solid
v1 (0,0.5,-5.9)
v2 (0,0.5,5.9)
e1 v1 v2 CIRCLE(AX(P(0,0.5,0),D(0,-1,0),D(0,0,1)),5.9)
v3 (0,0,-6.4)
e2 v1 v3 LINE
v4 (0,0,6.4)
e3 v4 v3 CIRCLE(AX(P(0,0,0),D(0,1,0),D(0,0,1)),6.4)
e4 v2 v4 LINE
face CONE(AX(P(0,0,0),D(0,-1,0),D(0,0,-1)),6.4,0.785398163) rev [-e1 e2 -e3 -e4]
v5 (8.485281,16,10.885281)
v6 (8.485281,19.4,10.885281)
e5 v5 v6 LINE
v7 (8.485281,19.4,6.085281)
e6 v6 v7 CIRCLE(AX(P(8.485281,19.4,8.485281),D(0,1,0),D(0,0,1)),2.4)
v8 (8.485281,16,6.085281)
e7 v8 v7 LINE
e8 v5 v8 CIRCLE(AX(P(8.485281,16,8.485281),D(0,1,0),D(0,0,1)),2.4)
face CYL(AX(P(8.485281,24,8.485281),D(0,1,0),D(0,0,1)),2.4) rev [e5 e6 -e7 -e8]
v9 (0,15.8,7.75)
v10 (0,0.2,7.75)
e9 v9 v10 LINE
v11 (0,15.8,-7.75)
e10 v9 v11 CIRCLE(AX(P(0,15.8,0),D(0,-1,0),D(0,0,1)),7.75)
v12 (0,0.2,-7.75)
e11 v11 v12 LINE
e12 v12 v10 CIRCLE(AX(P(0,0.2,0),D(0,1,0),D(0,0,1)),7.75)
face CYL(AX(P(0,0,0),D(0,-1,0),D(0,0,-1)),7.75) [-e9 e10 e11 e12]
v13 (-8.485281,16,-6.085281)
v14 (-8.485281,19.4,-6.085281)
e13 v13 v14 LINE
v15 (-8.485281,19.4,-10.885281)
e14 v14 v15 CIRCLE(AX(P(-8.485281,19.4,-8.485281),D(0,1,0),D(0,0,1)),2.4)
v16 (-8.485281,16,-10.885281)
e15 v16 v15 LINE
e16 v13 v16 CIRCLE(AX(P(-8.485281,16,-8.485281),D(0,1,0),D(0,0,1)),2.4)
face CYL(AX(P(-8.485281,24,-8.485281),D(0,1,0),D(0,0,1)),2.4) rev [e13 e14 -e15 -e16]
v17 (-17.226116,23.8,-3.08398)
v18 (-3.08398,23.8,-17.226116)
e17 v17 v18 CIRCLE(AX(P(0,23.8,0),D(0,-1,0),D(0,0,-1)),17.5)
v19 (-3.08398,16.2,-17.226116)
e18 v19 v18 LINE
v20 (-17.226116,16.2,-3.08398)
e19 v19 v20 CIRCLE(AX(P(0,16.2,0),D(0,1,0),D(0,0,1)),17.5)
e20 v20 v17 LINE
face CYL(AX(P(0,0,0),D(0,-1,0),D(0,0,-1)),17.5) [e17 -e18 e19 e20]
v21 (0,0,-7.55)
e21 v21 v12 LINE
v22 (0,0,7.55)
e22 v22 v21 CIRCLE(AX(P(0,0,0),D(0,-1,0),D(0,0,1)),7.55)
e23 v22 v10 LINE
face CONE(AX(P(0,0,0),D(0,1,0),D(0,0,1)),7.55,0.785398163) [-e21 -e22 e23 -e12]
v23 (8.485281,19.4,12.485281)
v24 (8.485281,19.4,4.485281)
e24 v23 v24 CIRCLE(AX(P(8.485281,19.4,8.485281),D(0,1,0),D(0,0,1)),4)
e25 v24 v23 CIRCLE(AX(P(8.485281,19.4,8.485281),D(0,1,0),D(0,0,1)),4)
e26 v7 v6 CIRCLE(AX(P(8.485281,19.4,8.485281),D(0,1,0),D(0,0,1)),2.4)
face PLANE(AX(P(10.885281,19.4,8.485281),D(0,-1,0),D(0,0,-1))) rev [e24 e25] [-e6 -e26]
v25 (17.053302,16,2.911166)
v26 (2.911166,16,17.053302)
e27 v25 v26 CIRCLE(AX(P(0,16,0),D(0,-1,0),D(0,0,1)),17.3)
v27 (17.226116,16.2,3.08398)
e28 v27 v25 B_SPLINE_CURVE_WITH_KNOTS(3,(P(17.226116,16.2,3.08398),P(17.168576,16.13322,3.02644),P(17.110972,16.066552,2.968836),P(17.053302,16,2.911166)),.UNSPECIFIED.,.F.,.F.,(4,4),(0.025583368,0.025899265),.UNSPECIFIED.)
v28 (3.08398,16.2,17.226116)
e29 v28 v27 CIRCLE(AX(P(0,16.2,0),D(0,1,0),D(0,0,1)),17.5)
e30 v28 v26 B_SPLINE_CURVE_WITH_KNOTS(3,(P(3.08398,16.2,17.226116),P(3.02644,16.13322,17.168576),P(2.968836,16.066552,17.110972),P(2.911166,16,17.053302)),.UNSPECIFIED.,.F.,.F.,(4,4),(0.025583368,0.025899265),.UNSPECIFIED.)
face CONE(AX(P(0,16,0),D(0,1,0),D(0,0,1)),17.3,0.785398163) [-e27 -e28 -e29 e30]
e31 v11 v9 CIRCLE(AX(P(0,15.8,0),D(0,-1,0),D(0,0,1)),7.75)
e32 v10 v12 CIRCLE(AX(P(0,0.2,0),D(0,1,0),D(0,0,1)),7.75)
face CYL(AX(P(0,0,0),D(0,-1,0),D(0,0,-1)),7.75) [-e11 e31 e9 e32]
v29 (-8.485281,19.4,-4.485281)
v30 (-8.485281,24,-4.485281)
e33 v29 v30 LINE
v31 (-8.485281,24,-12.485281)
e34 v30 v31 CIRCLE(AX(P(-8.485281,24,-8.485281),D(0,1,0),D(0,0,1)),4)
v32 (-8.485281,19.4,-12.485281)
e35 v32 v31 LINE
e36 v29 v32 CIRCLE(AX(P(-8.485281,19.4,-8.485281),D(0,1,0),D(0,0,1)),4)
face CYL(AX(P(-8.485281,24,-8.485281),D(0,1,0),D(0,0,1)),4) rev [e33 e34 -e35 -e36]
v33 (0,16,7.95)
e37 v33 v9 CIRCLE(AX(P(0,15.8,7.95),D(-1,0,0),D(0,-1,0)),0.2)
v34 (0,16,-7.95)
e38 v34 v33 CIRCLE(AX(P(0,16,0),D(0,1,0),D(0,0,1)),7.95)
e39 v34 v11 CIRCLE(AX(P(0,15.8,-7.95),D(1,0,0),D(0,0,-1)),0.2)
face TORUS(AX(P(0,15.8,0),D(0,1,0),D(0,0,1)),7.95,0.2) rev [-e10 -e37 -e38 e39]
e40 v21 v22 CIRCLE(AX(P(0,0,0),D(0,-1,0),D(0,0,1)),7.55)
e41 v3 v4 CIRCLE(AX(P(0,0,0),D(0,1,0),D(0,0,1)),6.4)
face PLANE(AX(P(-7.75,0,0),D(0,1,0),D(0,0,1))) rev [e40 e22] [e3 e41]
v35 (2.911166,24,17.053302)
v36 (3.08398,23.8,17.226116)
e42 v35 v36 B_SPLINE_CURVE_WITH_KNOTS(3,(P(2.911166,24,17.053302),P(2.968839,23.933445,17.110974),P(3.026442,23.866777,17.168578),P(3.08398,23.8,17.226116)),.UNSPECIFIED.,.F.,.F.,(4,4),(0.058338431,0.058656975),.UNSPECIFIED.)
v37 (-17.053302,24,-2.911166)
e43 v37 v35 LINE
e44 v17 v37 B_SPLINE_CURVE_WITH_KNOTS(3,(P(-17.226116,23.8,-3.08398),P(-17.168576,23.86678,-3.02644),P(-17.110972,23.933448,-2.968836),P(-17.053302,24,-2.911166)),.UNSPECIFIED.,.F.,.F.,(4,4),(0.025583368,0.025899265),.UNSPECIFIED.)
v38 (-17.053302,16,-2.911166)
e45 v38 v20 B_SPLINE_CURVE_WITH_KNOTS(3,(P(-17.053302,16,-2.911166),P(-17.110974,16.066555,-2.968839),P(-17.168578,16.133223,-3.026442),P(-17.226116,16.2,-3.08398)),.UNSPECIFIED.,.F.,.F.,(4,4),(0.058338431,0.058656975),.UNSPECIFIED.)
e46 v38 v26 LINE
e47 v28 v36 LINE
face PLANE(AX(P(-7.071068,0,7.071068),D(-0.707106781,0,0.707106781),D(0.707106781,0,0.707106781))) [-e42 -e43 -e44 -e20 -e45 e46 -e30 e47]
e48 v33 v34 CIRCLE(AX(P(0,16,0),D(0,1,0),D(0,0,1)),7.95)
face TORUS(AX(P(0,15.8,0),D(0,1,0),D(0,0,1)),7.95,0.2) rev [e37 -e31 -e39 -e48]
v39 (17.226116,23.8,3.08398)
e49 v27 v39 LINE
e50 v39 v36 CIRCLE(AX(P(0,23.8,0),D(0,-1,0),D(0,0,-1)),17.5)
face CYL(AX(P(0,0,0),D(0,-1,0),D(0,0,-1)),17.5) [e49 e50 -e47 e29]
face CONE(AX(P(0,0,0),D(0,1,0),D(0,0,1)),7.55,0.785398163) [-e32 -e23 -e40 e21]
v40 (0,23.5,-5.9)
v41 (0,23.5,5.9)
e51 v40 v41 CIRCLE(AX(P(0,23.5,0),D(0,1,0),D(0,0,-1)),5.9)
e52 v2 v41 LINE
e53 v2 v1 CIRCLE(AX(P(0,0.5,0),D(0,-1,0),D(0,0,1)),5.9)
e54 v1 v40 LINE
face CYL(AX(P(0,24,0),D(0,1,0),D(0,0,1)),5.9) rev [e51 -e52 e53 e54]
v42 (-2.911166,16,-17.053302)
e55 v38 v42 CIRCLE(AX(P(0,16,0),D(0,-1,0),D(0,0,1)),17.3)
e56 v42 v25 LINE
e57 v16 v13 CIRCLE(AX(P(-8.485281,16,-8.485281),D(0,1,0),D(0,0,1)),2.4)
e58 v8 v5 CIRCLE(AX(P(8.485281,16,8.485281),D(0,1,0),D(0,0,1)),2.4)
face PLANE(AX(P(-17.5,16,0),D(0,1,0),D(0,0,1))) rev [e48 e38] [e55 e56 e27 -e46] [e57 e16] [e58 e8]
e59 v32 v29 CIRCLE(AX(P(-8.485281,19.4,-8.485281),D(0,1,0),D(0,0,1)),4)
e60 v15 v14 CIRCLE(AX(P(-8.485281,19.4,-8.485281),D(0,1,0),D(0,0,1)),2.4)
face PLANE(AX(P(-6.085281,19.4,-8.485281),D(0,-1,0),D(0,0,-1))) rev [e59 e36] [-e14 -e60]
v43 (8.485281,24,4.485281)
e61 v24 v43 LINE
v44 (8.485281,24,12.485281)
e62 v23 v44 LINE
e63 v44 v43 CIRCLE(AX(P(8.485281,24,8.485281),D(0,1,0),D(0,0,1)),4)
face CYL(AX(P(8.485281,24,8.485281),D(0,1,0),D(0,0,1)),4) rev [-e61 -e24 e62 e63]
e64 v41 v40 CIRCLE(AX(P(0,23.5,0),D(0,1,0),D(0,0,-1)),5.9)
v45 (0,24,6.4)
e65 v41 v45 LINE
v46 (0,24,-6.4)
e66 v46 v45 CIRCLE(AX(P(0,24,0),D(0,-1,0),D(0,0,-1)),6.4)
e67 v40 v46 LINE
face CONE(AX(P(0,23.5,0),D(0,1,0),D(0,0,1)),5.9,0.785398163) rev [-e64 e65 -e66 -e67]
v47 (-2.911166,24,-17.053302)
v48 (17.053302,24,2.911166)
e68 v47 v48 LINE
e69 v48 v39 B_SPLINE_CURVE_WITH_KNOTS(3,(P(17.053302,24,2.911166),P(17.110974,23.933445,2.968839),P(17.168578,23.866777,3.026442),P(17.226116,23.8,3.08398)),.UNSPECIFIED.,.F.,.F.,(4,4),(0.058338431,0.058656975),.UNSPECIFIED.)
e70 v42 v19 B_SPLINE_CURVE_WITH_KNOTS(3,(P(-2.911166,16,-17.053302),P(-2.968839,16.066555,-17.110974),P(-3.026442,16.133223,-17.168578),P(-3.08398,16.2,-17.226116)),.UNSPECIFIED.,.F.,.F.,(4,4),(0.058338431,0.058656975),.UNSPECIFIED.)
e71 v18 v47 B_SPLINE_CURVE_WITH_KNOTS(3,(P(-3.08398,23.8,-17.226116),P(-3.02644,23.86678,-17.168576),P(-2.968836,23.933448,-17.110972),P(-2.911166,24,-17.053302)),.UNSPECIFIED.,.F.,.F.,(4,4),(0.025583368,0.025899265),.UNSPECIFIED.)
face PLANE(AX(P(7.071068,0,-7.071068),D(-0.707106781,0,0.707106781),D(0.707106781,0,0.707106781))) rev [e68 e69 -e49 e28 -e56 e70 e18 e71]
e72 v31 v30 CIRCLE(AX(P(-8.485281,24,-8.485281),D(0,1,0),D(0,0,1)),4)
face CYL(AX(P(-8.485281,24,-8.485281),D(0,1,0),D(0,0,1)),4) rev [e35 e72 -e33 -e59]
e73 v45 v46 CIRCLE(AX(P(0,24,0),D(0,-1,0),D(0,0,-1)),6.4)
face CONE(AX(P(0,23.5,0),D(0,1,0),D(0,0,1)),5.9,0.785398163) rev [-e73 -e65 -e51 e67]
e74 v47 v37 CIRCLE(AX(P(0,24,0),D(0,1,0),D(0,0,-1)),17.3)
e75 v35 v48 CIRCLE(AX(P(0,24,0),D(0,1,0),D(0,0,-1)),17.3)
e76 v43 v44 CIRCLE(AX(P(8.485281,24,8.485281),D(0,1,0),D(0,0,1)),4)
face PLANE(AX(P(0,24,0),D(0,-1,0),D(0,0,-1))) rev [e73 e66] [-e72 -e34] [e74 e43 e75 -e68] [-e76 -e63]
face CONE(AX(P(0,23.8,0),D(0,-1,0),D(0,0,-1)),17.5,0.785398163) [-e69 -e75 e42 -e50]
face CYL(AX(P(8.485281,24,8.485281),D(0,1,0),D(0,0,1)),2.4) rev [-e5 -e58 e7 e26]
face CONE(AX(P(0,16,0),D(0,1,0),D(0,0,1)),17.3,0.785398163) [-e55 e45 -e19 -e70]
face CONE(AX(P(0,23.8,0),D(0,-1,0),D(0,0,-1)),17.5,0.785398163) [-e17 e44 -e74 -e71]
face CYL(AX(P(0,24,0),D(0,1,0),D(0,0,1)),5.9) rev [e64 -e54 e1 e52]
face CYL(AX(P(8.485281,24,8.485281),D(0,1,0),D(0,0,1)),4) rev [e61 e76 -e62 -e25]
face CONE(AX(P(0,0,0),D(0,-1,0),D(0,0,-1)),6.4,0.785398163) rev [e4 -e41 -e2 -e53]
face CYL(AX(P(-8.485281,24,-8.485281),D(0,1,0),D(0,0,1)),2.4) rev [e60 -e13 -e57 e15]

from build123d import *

# Parameters (mm, degrees)
G1_4_TAPPED_HOLE1_D                               = 11.8
HOLE_SIZE_BASED_ON_SOCKET_HEAD_CAP_SC_D           = 4.8
HOLE_SIZE_BASED_ON_SOCKET_HEAD_CAP_SC_CBORE_D     = 8
HOLE_SIZE_BASED_ON_SOCKET_HEAD_CAP_SC_CBORE_DEPTH = 4.6
FILLET1_R                                         = 0.2
CHAMFER1_SIZE                                     = 0.2
CHAMFER2_SIZE                                     = 0.5
CUT_EXTRUDE1_DEPTH                                = 35.474628352


with BuildPart() as part:
    # Sketch2 → Revolve1 (revolve)
    with BuildSketch(Plane.XY, mode=Mode.PRIVATE) as revolve1_sk:
        Polygon((0, 24), (-17.5, 24), (-17.5, 16), (-7.75, 16), (-7.75, 0), (0, 0), align=None)
    revolve(revolve1_sk.sketch.rotate(Axis((0, 0, 0), (0, 1, 0)), 270), axis=Axis((0, 0, 0), (0, 1, 0)))

    # G1/4 Tapped Hole1 (through all)
    with Locations(Plane.ZX.offset(24)):
        with Locations((0, 0)):
            Hole(G1_4_TAPPED_HOLE1_D / 2)

    # Hole Size (% based on) Socket Head Cap Screw Type 1 (through all)
    with Locations(Plane(origin=(-8.485281374, 24, -8.485281374), x_dir=(0, 0, 1), z_dir=(0, 1, 0))):
        with Locations((0, 0), (16.970562748, 16.970562748)):
            CounterBoreHole(HOLE_SIZE_BASED_ON_SOCKET_HEAD_CAP_SC_D / 2, HOLE_SIZE_BASED_ON_SOCKET_HEAD_CAP_SC_CBORE_D / 2, HOLE_SIZE_BASED_ON_SOCKET_HEAD_CAP_SC_CBORE_DEPTH)

    # Fillet1
    fillet1_edges = [part.edges().sort_by_distance(p)[0] for p in [
        (0, 16, 7.75),
    ]]
    fillet(fillet1_edges, radius=FILLET1_R)

    # Chamfer1
    chamfer1_edges = [part.edges().sort_by_distance(p)[0] for p in [
        (0, 0, 7.75),
        (0, 16, 17.5),
        (0, 24, 17.5),
    ]]
    chamfer(chamfer1_edges, length=CHAMFER1_SIZE)

    # Chamfer2
    chamfer2_edges = [part.edges().sort_by_distance(p)[0] for p in [
        (0, 24, 5.9),
        (0, 0, 5.9),
    ]]
    chamfer(chamfer2_edges, length=CHAMFER2_SIZE)

    # Sketch7 → Cut-Extrude1 (cut, through all)
    with BuildSketch(Plane(origin=(0, 24, 0), x_dir=(1, 0, 0), z_dir=(0, 1, 0))):
        with BuildLine():
            Line((2.911166407, -17.053302031), (-17.053302031, 2.911166407))
            ThreePointArc((-17.053302031, 2.911166407), (-12.232947315, -12.232947315), (2.911166407, -17.053302031))
        make_face()
        with BuildLine():
            ThreePointArc((17.3, 0), (11.156317071, 13.222200627), (-2.911166407, 17.053302031))
            Line((-2.911166407, 17.053302031), (17.053302031, -2.911166407))
            ThreePointArc((17.053302031, -2.911166407), (17.238215179, -1.460800272), (17.3, 0))
        make_face()
        with BuildLine():
            Line((-17.053302031, 2.911166407), (-17.226115818, 3.083980194))
            ThreePointArc((-17.226115818, 3.083980194), (-12.374368671, -12.374368671), (3.083980194, -17.226115818))
            Line((3.083980194, -17.226115818), (2.911166407, -17.053302031))
            ThreePointArc((2.911166407, -17.053302031), (-12.232947315, -12.232947315), (-17.053302031, 2.911166407))
        make_face()
        with BuildLine():
            ThreePointArc((17.5, 0), (11.23121424, 13.42050024), (-3.083980194, 17.226115818))
            Line((-3.083980194, 17.226115818), (-2.911166407, 17.053302031))
            ThreePointArc((-2.911166407, 17.053302031), (11.156317071, 13.222200627), (17.3, 0))
            ThreePointArc((17.3, 0), (17.238215179, -1.460800272), (17.053302031, -2.911166407))
            Line((17.053302031, -2.911166407), (17.226115818, -3.083980194))
            ThreePointArc((17.226115818, -3.083980194), (17.431394477, -1.548058977), (17.5, 0))
        make_face()
    extrude(amount=-CUT_EXTRUDE1_DEPTH, mode=Mode.SUBTRACT)


solid = part.part
